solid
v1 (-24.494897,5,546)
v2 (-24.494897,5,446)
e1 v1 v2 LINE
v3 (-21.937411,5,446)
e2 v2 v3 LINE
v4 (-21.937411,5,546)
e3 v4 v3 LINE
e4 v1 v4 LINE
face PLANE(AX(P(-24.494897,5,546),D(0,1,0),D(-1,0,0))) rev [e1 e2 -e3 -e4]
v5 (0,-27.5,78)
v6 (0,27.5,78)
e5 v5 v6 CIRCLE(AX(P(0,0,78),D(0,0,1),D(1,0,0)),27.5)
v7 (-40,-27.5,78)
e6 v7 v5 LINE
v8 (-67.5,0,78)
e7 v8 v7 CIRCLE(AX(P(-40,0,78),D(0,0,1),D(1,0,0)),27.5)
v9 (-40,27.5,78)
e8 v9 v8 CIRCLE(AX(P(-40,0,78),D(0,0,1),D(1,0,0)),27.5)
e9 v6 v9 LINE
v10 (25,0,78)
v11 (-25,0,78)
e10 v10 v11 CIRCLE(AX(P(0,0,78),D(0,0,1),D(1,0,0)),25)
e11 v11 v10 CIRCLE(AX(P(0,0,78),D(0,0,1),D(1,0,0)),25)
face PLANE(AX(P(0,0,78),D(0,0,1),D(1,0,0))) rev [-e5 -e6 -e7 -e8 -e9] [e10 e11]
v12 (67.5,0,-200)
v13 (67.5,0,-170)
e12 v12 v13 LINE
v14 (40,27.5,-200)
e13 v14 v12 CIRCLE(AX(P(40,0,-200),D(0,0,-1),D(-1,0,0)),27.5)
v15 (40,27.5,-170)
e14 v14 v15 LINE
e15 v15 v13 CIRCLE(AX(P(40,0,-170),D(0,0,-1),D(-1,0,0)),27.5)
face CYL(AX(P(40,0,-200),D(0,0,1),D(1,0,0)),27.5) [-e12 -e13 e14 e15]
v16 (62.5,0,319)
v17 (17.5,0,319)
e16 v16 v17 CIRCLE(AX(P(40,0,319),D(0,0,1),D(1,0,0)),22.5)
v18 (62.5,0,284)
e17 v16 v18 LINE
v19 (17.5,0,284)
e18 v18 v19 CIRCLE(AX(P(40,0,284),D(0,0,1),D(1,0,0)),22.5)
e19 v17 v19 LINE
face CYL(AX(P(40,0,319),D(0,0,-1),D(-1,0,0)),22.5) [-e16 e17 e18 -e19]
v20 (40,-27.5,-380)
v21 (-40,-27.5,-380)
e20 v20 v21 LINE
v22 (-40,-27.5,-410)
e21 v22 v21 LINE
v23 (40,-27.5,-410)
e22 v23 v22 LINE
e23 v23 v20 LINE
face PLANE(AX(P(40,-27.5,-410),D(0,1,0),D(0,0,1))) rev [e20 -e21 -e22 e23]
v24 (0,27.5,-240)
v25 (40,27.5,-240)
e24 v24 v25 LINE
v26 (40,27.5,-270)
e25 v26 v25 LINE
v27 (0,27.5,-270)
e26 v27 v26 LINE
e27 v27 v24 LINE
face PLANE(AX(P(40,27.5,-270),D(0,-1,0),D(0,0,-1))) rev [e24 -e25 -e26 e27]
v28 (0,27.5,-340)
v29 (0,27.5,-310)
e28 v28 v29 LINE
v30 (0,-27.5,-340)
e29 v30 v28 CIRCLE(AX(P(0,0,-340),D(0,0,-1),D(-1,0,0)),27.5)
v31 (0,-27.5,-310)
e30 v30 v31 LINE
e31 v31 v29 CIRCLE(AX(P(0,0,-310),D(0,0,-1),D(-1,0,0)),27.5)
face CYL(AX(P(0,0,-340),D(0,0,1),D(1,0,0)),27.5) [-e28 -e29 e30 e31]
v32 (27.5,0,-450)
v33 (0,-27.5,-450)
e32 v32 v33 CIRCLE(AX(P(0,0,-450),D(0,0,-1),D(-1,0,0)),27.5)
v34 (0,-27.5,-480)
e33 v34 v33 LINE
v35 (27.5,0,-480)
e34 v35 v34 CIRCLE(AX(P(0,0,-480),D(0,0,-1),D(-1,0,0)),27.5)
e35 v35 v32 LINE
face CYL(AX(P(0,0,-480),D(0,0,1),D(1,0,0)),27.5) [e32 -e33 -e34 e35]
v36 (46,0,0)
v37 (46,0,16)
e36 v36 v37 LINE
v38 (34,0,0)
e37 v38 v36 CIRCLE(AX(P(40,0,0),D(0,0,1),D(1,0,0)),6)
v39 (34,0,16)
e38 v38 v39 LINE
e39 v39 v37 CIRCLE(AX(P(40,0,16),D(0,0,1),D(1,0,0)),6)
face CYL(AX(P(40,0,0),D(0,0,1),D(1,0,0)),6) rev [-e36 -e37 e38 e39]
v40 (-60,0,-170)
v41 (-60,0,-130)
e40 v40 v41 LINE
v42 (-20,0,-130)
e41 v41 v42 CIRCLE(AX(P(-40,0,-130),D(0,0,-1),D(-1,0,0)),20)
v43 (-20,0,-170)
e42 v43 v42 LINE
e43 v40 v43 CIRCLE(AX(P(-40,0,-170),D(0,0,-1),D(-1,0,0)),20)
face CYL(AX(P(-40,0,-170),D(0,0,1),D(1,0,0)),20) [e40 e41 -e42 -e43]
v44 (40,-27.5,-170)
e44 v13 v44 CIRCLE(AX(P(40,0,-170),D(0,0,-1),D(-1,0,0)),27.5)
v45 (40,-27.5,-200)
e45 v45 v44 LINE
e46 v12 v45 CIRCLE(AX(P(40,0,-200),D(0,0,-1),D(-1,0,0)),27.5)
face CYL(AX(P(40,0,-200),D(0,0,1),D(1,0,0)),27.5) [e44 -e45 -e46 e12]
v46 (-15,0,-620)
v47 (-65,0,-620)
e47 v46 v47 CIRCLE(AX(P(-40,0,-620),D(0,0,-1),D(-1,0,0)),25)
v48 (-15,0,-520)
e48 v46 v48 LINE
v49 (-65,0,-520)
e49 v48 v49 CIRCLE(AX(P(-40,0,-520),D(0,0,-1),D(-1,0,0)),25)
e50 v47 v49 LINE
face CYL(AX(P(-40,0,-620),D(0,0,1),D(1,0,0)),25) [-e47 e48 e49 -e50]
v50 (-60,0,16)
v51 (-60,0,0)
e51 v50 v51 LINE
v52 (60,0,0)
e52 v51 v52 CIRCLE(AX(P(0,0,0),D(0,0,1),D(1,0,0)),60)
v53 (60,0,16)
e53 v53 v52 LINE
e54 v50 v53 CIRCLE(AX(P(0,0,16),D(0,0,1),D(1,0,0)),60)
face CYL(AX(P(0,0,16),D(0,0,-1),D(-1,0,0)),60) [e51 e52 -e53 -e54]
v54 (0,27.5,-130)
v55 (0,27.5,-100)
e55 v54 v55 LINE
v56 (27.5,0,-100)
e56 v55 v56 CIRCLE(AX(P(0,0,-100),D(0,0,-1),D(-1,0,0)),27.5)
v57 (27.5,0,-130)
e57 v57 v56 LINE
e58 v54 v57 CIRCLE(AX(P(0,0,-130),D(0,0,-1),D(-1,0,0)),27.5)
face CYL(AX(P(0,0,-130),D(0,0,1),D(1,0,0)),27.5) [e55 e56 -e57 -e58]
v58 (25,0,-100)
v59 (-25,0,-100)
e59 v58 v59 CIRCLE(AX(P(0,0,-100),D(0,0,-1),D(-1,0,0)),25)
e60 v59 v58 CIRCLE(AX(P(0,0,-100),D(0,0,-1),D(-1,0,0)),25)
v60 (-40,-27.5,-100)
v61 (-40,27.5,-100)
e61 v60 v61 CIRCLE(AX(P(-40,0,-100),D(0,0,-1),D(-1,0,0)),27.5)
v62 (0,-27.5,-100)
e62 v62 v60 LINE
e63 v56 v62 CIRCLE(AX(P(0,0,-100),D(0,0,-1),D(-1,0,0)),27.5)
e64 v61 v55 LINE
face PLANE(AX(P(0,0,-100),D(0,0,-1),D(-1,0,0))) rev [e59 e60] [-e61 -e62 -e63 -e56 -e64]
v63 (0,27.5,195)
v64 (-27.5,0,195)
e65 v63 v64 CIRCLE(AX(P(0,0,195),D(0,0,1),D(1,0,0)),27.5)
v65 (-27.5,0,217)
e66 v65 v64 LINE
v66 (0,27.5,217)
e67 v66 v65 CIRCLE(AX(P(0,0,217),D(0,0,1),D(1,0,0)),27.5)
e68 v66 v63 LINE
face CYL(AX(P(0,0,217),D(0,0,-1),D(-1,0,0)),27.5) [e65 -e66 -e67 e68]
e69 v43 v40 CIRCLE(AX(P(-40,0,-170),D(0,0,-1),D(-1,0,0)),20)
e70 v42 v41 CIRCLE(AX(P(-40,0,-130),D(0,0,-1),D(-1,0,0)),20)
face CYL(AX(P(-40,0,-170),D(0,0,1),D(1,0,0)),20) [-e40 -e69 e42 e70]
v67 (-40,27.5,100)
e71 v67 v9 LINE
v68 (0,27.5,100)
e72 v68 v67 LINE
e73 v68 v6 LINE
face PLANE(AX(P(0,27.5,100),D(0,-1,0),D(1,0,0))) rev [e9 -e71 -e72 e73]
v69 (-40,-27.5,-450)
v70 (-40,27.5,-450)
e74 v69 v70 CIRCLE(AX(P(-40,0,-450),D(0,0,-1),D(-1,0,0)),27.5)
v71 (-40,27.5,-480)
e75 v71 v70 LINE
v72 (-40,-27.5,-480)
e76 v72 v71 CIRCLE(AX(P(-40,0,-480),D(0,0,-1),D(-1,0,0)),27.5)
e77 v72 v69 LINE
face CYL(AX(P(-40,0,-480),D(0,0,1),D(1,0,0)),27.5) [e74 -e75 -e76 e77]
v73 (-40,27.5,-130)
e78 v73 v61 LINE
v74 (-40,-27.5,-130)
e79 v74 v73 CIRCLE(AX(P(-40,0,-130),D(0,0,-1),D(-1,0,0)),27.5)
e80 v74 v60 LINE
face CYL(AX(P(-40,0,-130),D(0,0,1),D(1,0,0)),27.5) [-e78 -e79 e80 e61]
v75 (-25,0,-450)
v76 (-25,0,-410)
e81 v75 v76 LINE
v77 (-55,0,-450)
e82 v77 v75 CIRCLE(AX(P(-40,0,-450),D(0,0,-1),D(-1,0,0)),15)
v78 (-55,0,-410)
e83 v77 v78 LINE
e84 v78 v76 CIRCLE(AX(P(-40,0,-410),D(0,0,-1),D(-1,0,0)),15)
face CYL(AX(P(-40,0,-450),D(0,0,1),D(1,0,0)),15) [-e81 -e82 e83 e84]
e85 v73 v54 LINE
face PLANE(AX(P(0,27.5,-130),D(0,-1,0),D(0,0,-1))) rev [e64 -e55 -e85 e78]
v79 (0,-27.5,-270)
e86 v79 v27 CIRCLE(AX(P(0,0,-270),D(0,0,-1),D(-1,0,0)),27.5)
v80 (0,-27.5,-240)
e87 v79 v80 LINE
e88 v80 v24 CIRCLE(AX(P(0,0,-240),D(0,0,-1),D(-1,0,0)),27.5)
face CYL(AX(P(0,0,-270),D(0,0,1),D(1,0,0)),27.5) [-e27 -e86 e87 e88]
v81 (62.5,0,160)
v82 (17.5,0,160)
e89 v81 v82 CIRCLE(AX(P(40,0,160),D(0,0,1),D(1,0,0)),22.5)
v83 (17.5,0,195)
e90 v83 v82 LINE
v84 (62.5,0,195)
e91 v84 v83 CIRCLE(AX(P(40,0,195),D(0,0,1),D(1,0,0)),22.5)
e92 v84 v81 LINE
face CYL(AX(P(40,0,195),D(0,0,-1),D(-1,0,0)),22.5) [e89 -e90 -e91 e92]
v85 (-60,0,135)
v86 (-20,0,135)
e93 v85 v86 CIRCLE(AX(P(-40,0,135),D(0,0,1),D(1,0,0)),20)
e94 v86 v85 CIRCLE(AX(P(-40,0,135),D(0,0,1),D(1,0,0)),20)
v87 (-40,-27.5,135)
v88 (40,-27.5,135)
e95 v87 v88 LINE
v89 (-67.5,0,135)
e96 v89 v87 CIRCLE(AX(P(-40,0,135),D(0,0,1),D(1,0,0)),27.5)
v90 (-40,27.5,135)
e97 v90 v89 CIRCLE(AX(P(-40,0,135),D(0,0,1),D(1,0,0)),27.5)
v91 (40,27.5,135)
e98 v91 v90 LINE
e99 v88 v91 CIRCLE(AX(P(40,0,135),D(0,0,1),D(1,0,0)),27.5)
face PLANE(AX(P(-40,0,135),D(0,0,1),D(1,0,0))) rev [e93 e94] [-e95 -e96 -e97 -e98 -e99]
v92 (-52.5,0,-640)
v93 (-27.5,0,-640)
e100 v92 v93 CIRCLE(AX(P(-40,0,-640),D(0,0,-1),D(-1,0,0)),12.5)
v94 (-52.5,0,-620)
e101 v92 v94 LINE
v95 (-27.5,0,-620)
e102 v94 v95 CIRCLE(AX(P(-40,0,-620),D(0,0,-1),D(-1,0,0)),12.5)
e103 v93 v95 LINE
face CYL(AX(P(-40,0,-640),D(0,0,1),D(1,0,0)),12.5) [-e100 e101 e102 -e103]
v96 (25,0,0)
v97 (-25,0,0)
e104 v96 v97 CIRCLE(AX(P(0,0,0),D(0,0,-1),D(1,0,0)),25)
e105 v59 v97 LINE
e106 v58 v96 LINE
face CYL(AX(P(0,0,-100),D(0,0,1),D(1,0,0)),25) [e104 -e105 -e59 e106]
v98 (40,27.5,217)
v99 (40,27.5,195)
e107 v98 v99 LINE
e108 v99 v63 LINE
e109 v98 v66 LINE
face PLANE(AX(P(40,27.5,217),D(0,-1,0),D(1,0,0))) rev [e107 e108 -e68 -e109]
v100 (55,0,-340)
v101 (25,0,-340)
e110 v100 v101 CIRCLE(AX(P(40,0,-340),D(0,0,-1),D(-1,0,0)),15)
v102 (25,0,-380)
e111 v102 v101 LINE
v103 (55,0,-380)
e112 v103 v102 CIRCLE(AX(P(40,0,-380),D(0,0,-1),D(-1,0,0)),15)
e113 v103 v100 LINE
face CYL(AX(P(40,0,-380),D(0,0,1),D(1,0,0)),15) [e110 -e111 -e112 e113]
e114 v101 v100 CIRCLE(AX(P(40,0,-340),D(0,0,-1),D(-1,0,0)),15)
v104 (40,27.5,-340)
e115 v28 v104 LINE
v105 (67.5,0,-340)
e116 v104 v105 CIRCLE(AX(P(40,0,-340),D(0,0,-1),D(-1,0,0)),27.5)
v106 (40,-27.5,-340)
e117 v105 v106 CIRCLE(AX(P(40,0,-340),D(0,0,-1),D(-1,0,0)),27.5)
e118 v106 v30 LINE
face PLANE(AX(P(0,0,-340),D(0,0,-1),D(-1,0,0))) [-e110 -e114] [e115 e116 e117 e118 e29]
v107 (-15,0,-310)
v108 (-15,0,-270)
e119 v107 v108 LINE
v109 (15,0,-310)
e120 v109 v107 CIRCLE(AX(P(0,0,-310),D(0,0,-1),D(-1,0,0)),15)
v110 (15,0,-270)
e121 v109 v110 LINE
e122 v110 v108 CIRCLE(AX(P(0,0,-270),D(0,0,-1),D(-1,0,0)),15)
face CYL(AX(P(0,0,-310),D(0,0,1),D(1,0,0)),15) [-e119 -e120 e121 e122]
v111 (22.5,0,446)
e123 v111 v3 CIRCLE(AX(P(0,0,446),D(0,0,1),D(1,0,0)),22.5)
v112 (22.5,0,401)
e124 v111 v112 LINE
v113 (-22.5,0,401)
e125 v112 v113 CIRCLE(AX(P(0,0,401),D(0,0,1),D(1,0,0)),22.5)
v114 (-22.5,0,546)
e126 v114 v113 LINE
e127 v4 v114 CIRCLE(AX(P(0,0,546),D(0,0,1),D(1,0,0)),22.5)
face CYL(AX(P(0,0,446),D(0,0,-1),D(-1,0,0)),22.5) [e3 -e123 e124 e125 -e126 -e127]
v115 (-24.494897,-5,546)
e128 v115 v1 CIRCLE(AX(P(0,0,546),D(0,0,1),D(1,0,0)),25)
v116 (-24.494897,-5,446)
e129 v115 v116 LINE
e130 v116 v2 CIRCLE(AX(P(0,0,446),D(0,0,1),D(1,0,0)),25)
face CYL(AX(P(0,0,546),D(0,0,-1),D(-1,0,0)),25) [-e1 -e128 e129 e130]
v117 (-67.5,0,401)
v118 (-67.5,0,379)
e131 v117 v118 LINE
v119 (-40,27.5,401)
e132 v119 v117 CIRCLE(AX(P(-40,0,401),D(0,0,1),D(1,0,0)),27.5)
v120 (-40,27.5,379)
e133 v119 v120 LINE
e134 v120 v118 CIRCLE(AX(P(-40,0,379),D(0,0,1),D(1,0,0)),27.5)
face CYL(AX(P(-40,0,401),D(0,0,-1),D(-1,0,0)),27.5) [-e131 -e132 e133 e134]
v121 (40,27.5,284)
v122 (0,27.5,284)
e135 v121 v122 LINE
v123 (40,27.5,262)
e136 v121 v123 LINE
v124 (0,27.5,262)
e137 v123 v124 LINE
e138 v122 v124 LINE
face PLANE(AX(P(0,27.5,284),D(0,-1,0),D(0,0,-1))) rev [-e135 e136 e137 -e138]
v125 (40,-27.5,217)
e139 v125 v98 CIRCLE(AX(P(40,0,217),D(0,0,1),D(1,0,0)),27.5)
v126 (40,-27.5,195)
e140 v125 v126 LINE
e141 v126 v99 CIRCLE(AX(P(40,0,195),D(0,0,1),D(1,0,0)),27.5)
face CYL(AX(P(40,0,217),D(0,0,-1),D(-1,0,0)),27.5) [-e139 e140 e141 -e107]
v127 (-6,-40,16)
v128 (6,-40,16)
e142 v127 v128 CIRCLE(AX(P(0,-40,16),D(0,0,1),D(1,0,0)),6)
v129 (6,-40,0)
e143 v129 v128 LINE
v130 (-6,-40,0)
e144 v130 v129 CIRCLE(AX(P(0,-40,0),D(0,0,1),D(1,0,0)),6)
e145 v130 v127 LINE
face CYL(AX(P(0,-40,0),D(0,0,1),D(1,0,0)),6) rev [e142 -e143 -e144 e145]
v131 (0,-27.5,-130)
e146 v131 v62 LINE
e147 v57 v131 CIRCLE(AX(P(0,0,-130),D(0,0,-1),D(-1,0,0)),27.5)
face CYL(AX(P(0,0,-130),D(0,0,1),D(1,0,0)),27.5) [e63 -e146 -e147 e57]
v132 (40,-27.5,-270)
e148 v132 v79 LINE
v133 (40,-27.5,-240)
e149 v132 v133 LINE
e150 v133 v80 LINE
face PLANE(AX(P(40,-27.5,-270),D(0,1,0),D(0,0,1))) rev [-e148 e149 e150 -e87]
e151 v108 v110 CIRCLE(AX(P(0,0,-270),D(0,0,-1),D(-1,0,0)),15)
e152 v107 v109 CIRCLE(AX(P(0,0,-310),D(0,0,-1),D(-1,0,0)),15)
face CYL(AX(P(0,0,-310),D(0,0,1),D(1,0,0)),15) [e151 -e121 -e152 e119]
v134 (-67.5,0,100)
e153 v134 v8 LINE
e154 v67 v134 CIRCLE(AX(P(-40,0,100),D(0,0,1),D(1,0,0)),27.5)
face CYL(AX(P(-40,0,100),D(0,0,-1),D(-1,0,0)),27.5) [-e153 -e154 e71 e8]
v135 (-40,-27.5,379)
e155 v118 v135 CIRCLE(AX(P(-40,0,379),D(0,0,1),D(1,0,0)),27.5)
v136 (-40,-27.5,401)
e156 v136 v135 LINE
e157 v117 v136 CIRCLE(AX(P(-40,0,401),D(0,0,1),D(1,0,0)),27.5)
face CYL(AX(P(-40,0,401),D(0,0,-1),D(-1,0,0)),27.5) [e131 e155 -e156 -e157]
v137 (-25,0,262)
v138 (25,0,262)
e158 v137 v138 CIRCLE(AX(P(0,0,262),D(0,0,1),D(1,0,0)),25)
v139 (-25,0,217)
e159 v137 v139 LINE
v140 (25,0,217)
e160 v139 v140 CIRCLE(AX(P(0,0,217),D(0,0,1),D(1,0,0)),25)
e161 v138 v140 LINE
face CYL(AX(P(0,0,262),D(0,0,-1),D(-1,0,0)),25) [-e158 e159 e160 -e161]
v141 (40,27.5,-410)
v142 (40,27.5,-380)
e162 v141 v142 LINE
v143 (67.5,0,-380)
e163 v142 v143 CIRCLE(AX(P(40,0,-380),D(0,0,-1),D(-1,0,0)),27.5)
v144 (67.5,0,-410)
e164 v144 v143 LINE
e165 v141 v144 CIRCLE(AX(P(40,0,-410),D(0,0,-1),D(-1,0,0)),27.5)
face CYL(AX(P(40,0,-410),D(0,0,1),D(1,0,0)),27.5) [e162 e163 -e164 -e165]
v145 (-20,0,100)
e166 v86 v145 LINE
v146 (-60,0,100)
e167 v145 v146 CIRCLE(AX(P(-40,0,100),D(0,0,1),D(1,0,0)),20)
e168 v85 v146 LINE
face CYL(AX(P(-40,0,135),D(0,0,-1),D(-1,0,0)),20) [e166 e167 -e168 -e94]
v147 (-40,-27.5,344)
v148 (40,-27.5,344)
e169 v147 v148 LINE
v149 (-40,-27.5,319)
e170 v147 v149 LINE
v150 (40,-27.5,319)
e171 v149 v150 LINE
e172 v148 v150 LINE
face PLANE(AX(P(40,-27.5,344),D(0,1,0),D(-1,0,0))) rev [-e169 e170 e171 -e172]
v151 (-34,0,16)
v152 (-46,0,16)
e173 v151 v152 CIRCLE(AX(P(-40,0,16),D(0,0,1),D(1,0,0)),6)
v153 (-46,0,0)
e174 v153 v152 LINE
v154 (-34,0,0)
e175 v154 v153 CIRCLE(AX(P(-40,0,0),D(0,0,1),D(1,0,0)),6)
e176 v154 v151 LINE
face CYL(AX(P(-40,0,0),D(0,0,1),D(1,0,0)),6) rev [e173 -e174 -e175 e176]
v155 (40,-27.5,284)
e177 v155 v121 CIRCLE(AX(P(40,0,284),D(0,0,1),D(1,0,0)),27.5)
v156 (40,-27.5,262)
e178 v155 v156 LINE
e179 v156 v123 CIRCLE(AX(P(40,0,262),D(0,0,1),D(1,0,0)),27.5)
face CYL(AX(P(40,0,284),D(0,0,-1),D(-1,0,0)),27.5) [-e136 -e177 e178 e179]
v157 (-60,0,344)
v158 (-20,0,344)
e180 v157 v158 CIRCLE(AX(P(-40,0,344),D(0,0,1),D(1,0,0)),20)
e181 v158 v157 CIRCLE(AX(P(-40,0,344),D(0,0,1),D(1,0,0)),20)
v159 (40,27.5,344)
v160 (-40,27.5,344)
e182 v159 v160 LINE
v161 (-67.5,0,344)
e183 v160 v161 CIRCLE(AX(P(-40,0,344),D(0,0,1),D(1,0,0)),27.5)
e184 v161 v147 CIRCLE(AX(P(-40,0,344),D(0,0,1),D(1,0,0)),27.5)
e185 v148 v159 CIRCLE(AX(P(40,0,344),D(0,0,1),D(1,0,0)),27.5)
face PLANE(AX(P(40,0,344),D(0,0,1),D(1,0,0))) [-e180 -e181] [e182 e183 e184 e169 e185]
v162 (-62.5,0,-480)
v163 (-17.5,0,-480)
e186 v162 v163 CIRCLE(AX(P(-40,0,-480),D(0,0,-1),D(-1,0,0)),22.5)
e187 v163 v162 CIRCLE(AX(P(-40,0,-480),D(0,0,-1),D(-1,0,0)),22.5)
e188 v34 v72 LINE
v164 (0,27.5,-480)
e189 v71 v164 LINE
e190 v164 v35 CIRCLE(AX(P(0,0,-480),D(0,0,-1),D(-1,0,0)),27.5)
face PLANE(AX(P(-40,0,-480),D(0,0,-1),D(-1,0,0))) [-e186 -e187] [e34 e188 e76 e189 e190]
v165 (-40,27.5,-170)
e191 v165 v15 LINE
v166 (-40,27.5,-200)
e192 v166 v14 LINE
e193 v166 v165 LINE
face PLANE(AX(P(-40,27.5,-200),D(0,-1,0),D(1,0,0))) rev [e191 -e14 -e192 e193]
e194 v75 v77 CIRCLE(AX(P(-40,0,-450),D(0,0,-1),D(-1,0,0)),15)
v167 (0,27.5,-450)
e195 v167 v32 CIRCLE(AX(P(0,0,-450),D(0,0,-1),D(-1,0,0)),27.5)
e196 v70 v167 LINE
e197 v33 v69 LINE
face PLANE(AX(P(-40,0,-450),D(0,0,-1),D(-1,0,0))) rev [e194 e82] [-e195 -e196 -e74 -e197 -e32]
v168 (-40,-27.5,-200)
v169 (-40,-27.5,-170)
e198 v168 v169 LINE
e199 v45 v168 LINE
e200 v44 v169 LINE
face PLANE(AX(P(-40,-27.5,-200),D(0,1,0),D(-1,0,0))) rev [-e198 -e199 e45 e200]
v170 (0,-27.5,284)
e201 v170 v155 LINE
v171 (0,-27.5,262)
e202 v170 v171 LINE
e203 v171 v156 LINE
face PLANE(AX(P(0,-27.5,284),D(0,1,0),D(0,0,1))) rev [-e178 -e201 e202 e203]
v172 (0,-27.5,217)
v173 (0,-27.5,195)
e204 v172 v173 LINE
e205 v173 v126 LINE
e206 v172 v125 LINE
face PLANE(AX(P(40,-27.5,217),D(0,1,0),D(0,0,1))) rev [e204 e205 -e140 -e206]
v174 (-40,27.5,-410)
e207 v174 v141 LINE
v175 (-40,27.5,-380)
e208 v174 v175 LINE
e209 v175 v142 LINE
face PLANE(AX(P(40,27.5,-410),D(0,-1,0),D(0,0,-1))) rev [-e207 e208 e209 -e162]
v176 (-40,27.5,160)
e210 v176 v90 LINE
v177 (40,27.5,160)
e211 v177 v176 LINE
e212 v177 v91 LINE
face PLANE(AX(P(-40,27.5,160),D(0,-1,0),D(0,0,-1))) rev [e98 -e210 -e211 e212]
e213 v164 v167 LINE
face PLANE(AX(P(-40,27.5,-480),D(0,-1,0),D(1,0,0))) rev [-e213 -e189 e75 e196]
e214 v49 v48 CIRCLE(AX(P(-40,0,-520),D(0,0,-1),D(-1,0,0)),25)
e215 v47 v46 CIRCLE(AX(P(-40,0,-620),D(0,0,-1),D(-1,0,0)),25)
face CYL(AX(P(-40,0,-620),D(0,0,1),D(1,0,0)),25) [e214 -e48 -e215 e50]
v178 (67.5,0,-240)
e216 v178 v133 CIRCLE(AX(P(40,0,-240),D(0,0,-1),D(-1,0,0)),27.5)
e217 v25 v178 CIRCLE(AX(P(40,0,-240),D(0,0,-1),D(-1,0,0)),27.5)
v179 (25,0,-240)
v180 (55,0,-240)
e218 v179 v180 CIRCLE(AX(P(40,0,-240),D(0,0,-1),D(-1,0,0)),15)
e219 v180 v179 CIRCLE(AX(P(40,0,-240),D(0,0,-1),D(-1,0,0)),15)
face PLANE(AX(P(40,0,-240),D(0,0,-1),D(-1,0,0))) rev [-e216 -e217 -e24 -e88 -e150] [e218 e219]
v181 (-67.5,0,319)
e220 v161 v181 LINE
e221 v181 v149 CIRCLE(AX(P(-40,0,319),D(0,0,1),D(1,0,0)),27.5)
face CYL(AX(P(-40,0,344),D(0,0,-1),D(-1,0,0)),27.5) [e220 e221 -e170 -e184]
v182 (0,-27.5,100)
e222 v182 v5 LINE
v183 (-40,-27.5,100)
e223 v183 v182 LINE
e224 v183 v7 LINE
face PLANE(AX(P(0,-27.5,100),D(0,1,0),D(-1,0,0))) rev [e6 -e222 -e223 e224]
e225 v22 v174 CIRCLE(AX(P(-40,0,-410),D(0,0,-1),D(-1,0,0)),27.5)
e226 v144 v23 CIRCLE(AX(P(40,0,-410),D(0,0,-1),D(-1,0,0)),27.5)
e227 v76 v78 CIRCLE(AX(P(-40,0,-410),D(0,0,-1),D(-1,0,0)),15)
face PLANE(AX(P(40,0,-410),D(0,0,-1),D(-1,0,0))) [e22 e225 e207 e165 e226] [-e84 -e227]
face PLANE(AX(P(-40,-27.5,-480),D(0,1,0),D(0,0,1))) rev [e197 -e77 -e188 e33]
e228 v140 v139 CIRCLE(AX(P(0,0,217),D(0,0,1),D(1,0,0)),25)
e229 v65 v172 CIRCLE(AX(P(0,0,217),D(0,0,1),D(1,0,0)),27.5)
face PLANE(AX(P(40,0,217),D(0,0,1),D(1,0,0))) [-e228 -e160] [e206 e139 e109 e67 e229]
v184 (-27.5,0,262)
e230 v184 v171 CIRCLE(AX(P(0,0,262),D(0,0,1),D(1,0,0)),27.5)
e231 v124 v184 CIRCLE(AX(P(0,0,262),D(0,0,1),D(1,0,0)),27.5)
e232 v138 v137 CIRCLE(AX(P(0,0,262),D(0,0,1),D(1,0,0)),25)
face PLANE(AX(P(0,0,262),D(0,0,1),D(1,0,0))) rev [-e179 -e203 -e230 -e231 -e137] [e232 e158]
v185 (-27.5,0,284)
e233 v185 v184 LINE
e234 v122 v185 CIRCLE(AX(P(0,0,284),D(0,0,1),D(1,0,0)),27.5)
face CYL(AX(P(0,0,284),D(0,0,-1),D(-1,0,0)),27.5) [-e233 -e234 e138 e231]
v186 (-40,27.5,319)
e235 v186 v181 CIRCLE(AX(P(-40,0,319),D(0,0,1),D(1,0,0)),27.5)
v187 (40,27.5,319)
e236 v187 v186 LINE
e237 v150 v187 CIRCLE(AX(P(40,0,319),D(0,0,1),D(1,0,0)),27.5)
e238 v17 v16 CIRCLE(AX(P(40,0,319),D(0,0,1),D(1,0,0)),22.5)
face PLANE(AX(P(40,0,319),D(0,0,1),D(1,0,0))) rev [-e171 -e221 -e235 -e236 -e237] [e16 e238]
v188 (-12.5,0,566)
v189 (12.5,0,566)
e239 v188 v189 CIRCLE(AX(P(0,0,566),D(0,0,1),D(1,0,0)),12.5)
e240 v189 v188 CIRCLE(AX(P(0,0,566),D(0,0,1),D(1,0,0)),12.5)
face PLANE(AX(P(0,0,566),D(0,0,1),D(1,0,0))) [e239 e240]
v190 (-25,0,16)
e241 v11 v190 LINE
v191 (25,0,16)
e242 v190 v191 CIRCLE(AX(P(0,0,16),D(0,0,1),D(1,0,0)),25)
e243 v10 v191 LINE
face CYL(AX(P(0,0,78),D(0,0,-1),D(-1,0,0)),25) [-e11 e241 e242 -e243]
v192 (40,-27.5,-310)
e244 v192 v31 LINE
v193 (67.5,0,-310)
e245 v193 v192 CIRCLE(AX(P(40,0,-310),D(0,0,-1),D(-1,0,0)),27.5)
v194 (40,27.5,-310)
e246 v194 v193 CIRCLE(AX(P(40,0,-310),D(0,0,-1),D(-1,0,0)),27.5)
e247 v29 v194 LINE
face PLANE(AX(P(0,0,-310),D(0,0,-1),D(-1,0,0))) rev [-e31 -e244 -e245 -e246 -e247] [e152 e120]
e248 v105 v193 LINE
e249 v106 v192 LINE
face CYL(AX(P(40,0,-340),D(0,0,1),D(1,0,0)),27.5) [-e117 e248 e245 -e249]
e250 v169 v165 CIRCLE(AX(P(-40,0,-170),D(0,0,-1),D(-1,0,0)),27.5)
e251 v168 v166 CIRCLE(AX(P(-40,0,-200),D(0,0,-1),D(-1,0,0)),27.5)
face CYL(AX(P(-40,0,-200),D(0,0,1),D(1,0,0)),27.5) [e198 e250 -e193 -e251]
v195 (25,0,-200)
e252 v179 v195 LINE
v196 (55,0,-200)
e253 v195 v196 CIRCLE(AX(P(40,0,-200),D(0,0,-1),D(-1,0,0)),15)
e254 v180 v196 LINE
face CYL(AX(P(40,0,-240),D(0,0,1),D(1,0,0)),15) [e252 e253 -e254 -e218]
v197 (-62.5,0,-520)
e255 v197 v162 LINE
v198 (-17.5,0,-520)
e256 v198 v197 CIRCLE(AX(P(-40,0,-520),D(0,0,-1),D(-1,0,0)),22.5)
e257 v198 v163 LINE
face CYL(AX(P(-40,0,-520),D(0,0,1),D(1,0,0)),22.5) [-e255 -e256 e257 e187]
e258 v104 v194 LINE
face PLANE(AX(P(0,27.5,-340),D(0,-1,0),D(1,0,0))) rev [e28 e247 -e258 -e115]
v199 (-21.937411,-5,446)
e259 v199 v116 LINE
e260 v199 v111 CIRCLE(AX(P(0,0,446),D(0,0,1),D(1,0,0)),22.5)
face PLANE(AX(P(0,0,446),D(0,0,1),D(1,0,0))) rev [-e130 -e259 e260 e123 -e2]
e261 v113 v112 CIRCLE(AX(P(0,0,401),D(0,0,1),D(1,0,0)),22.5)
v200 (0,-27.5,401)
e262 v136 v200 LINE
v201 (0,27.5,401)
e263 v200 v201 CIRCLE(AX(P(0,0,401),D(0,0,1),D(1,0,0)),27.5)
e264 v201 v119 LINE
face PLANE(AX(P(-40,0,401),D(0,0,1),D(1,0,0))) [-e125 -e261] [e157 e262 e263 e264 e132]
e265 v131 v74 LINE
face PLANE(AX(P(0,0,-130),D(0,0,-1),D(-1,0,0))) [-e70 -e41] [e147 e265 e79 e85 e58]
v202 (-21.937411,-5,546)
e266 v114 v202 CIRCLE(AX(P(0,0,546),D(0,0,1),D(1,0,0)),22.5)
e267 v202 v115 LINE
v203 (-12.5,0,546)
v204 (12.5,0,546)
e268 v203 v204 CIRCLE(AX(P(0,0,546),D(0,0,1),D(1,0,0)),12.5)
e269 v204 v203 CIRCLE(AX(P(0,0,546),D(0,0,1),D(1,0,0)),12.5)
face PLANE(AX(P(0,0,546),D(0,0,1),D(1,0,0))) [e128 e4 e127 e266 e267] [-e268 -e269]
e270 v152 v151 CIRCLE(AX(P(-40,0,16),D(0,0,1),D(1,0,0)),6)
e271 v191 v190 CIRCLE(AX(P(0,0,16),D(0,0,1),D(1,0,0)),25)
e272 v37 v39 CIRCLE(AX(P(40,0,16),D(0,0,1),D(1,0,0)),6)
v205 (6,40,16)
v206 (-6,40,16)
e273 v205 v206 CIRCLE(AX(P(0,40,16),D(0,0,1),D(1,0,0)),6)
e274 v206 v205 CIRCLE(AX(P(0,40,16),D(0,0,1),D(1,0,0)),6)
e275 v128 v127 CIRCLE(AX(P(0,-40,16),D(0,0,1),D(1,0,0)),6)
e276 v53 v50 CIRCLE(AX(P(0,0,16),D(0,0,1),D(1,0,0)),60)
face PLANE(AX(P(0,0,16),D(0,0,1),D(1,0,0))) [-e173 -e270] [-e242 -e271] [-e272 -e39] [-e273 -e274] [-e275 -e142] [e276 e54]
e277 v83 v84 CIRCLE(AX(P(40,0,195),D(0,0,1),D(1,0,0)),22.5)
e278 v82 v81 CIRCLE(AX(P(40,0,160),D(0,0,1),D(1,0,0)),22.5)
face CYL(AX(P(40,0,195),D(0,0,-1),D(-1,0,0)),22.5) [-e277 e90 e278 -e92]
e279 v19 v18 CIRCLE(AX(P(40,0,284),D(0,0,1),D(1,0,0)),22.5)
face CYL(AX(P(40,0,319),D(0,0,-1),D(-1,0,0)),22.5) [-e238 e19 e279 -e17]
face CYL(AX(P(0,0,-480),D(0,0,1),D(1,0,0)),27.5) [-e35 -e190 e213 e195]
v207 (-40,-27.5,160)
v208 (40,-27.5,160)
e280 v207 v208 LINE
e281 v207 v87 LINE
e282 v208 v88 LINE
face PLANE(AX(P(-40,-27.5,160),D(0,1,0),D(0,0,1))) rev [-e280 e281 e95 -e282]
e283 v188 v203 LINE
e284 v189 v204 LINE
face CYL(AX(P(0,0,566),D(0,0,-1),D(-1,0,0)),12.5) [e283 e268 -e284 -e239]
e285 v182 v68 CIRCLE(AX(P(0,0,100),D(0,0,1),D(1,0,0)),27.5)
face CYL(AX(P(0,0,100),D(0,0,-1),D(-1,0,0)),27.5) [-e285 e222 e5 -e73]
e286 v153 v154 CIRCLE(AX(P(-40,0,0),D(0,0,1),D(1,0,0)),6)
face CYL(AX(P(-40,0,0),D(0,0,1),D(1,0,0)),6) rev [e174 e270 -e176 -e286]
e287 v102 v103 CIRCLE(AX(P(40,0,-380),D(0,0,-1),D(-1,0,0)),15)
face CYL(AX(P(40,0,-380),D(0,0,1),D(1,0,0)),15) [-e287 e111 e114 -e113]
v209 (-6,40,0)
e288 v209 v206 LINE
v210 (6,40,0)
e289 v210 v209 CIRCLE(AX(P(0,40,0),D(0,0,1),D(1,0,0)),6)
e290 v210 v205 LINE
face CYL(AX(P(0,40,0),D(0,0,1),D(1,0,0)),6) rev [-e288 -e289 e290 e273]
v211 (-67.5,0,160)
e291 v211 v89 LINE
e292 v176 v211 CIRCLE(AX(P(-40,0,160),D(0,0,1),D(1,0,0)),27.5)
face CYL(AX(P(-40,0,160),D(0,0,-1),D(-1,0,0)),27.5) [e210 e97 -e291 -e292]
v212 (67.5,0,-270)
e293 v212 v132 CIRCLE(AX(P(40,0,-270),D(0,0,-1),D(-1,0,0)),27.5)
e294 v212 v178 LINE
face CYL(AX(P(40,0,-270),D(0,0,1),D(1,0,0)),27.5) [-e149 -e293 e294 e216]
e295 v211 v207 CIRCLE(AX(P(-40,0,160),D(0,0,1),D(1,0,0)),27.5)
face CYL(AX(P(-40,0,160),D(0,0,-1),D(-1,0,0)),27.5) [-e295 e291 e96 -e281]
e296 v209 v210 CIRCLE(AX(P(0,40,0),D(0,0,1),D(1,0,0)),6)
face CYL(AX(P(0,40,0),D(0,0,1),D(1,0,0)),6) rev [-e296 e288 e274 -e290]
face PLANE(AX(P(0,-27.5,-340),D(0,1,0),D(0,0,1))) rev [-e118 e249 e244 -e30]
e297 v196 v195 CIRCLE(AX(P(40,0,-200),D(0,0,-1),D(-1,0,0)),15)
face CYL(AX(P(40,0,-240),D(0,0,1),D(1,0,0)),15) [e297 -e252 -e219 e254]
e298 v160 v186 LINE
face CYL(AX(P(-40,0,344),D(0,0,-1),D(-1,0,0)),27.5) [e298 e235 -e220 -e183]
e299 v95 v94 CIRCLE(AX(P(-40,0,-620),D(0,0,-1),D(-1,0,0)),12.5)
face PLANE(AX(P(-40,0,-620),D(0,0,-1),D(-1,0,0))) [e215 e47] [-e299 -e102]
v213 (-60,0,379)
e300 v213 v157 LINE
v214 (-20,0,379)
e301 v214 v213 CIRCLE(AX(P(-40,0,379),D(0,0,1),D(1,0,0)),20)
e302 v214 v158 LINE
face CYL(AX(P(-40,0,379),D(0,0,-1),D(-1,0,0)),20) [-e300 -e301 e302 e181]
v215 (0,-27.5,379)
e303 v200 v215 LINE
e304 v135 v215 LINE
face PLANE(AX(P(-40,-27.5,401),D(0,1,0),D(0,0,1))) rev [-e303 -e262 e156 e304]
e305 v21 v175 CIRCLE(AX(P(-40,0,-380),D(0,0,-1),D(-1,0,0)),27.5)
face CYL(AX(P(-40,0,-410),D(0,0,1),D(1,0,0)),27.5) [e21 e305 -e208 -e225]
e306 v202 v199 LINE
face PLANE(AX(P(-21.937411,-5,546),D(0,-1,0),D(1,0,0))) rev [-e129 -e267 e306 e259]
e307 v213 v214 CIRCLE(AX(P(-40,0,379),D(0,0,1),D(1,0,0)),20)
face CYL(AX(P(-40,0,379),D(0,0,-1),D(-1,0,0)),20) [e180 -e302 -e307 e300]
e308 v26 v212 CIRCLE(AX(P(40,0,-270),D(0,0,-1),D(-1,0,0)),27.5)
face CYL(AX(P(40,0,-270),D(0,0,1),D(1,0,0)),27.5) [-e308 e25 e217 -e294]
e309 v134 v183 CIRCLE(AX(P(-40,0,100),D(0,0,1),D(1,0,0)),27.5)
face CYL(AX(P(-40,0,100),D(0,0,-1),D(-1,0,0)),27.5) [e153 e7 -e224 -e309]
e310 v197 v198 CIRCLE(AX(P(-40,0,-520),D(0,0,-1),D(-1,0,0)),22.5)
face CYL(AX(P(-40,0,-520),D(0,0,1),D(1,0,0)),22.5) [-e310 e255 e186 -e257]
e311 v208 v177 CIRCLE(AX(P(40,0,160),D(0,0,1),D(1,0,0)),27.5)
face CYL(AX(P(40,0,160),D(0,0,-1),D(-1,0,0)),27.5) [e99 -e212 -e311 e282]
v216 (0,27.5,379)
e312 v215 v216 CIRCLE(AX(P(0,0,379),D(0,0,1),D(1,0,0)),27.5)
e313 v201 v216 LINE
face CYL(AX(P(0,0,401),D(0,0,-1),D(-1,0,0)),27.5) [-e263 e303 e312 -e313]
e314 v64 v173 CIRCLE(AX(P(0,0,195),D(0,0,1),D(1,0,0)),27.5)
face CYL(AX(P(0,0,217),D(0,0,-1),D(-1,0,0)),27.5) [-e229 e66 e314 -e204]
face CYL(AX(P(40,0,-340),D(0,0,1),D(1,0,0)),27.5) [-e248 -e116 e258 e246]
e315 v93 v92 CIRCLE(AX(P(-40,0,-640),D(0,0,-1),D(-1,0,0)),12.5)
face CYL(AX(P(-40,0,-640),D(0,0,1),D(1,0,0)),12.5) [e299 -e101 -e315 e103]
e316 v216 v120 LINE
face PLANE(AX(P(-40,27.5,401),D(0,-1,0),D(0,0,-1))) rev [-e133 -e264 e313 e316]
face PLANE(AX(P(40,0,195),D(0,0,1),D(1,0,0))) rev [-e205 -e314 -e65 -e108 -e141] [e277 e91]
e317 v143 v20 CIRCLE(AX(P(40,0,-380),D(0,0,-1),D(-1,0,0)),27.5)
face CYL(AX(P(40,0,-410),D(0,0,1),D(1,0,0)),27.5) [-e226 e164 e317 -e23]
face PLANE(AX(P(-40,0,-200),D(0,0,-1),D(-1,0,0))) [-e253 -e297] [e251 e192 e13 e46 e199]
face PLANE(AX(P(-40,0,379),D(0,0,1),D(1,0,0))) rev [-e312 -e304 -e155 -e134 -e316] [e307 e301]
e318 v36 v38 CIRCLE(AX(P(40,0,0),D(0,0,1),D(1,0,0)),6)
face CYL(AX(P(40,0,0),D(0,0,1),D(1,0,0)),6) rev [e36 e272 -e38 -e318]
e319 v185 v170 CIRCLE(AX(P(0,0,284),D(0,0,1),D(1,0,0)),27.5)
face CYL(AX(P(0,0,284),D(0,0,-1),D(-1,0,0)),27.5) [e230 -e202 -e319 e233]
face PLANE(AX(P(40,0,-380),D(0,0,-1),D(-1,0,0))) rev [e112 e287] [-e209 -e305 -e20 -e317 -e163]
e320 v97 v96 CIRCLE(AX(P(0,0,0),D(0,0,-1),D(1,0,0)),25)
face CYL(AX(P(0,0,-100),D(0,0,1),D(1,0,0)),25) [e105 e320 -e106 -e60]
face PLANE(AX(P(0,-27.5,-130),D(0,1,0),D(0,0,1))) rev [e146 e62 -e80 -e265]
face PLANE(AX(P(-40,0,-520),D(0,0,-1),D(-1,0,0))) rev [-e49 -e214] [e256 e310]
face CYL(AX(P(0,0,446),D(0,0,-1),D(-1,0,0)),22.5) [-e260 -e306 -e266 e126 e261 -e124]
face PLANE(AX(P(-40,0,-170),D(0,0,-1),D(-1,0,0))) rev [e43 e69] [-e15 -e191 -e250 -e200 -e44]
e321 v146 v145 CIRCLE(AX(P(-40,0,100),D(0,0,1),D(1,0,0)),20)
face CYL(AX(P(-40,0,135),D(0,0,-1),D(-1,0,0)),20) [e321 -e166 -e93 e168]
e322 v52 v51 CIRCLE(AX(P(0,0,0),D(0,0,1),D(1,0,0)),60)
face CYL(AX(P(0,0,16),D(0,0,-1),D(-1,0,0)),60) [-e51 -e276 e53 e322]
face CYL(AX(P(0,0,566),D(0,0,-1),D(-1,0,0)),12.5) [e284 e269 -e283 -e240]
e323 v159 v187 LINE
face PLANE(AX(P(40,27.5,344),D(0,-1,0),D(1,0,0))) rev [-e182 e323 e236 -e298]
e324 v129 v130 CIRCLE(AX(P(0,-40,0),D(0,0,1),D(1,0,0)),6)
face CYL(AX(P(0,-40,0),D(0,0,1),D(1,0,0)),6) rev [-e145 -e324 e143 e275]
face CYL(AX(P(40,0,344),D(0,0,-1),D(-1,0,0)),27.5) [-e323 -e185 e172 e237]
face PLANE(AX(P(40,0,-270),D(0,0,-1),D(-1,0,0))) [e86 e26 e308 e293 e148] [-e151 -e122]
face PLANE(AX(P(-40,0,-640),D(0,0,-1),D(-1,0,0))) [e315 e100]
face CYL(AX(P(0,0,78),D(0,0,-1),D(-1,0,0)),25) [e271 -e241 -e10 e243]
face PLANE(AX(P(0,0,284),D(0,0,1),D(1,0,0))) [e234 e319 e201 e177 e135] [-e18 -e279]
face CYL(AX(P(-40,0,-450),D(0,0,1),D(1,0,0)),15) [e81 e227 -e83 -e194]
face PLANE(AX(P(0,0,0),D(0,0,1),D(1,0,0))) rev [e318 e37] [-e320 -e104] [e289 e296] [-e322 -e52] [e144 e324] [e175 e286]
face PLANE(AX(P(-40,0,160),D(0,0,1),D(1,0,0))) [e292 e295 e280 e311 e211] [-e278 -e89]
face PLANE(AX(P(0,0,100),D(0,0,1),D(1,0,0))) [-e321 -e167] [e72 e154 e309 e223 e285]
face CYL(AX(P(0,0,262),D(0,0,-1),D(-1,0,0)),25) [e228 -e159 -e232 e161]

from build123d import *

# Parameters (mm, degrees)
CENTRE_FLANGE_SKETCH_R  = 60
CENTRE_FLANGE_120_DEPTH = 16
FLANGE_HOLES_SKETCH_R   = 6
FLANGE_HOLES_12_DEPTH   = 87.34813258
A_JOURNAL_1_SKETCH_R    = 25
A_JOURNAL_1_50_DEPTH    = 62
A_WEB_1_DEPTH           = 22
A_PIN_1_SKETCH_R        = 20
A_PIN_1_40_DEPTH        = 35
A_WEB_2_DEPTH           = 25
A_PIN_2_SKETCH_R        = 22.5
A_PIN_2_45_DEPTH        = 35
A_WEB_3_DEPTH           = 22
A_JOURNAL_2_SKETCH_R    = 25
A_JOURNAL_2_50_DEPTH    = 45
A_WEB_4_DEPTH           = 22
A_PIN_3_SKETCH_R        = 22.5
A_PIN_3_45_DEPTH        = 35
A_WEB_5_DEPTH           = 25
A_PIN_4_SKETCH_R        = 20
A_PIN_4_40_DEPTH        = 35
A_WEB_6_DEPTH           = 22
A_JOURNAL_3_SKETCH_R    = 22.5
A_JOURNAL_3_45_DEPTH    = 45
A_SHAFT_END_DEPTH       = 100
A_END_SPIGOT_SKETCH_R   = 12.5
A_END_SPIGOT_25_DEPTH   = 20
B_START                 = 100
B_JOURNAL_1_SKETCH_R    = 25
B_JOURNAL_1_50_DEPTH    = 100
B_START_2               = 30
B_WEB_1_DEPTH           = 30
B_START_3               = 40
B_PIN_1_SKETCH_R        = 20
B_PIN_1_40_DEPTH        = 40
B_WEB_2_DEPTH           = 30
B_JOURNAL_2_SKETCH_R    = 15
B_JOURNAL_2_30_DEPTH    = 40
B_WEB_3_DEPTH           = 30
B_JOURNAL_3_SKETCH_R    = 15
B_JOURNAL_3_30_DEPTH    = 40
B_WEB_4_DEPTH           = 30
B_JOURNAL_4_SKETCH_R    = 15
B_JOURNAL_4_30_DEPTH    = 40
B_WEB_5_DEPTH           = 30
B_JOURNAL_5_SKETCH_R    = 15
B_JOURNAL_5_30_DEPTH    = 40
B_WEB_6_DEPTH           = 30
B_JOURNAL_6_SKETCH_R    = 22.5
B_JOURNAL_6_45_DEPTH    = 40
B_SHAFT_END_SKETCH_R    = 25
B_SHAFT_END_50_DEPTH    = 100
B_END_SPIGOT_SKETCH_R   = 12.5
B_END_SPIGOT_25_DEPTH   = 20


with BuildPart() as part:
    # Centre Flange Sketch → Centre Flange Ø120 (new body)
    with BuildSketch(Plane.XY):
        Circle(CENTRE_FLANGE_SKETCH_R)
    extrude(amount=CENTRE_FLANGE_120_DEPTH)

    # Flange Holes Sketch → Flange Holes Ø12 (cut, through all)
    with BuildSketch(Plane.XY.offset(16)):
        with Locations((0, 40)):
            Circle(FLANGE_HOLES_SKETCH_R)
        with Locations((40, 0)):
            Circle(FLANGE_HOLES_SKETCH_R)
        with Locations((0, -40)):
            Circle(FLANGE_HOLES_SKETCH_R)
        with Locations((-40, 0)):
            Circle(FLANGE_HOLES_SKETCH_R)
    extrude(amount=-FLANGE_HOLES_12_DEPTH, mode=Mode.SUBTRACT)

    # A Journal 1 Sketch → A Journal 1 Ø50 (add)
    with BuildSketch(Plane.XY.offset(16)):
        Circle(A_JOURNAL_1_SKETCH_R)
    extrude(amount=A_JOURNAL_1_50_DEPTH)

    # A Web 1 Sketch → A Web 1 (add)
    with BuildSketch(Plane.XY.offset(78)):
        with BuildLine():
            Line((0, -27.5), (-40, -27.5))
            ThreePointArc((-40, -27.5), (-67.5, 0), (-40, 27.5))
            Line((-40, 27.5), (0, 27.5))
            ThreePointArc((0, 27.5), (27.5, 0), (0, -27.5))
        make_face()
    extrude(amount=A_WEB_1_DEPTH)

    # A Pin 1 Sketch → A Pin 1 Ø40 (add)
    with BuildSketch(Plane.XY.offset(100)):
        with Locations((-40, 0)):
            Circle(A_PIN_1_SKETCH_R)
    extrude(amount=A_PIN_1_40_DEPTH)

    # A Web 2 Sketch → A Web 2 (add)
    with BuildSketch(Plane.XY.offset(135)):
        with BuildLine():
            Line((-40, 27.5), (40, 27.5))
            ThreePointArc((40, 27.5), (67.5, 0), (40, -27.5))
            Line((40, -27.5), (-40, -27.5))
            ThreePointArc((-40, -27.5), (-67.5, 0), (-40, 27.5))
        make_face()
    extrude(amount=A_WEB_2_DEPTH)

    # A Pin 2 Sketch → A Pin 2 Ø45 (add)
    with BuildSketch(Plane.XY.offset(160)):
        with Locations((40, 0)):
            Circle(A_PIN_2_SKETCH_R)
    extrude(amount=A_PIN_2_45_DEPTH)

    # A Web 3 Sketch → A Web 3 (add)
    with BuildSketch(Plane.XY.offset(195)):
        with BuildLine():
            Line((40, -27.5), (0, -27.5))
            ThreePointArc((0, -27.5), (-27.5, 0), (0, 27.5))
            Line((0, 27.5), (40, 27.5))
            ThreePointArc((40, 27.5), (67.5, 0), (40, -27.5))
        make_face()
    extrude(amount=A_WEB_3_DEPTH)

    # A Journal 2 Sketch → A Journal 2 Ø50 (add)
    with BuildSketch(Plane.XY.offset(217)):
        Circle(A_JOURNAL_2_SKETCH_R)
    extrude(amount=A_JOURNAL_2_50_DEPTH)

    # A Web 4 Sketch → A Web 4 (add)
    with BuildSketch(Plane.XY.offset(262)):
        with BuildLine():
            Line((0, 27.5), (40, 27.5))
            ThreePointArc((40, 27.5), (67.5, 0), (40, -27.5))
            Line((40, -27.5), (0, -27.5))
            ThreePointArc((0, -27.5), (-27.5, 0), (0, 27.5))
        make_face()
    extrude(amount=A_WEB_4_DEPTH)

    # A Pin 3 Sketch → A Pin 3 Ø45 (add)
    with BuildSketch(Plane.XY.offset(284)):
        with Locations((40, 0)):
            Circle(A_PIN_3_SKETCH_R)
    extrude(amount=A_PIN_3_45_DEPTH)

    # A Web 5 Sketch → A Web 5 (add)
    with BuildSketch(Plane.XY.offset(319)):
        with BuildLine():
            Line((40, -27.5), (-40, -27.5))
            ThreePointArc((-40, -27.5), (-67.5, 0), (-40, 27.5))
            Line((-40, 27.5), (40, 27.5))
            ThreePointArc((40, 27.5), (67.5, 0), (40, -27.5))
        make_face()
    extrude(amount=A_WEB_5_DEPTH)

    # A Pin 4 Sketch → A Pin 4 Ø40 (add)
    with BuildSketch(Plane.XY.offset(344)):
        with Locations((-40, 0)):
            Circle(A_PIN_4_SKETCH_R)
    extrude(amount=A_PIN_4_40_DEPTH)

    # A Web 6 Sketch → A Web 6 (add)
    with BuildSketch(Plane.XY.offset(379)):
        with BuildLine():
            Line((-40, 27.5), (0, 27.5))
            ThreePointArc((0, 27.5), (27.5, 0), (0, -27.5))
            Line((0, -27.5), (-40, -27.5))
            ThreePointArc((-40, -27.5), (-67.5, 0), (-40, 27.5))
        make_face()
    extrude(amount=A_WEB_6_DEPTH)

    # A Journal 3 Sketch → A Journal 3 Ø45 (add)
    with BuildSketch(Plane.XY.offset(401)):
        with Locations(Location((0, 0, 0), (0, 0, 180))):
            Circle(A_JOURNAL_3_SKETCH_R)
    extrude(amount=A_JOURNAL_3_45_DEPTH)

    # A Shaft End Sketch → A Shaft End (add)
    with BuildSketch(Plane.XY.offset(446)):
        with BuildLine():
            Line((-24.494897428, 5), (-21.937410968, 5))
            ThreePointArc((-21.937410968, 5), (-22.5, 0), (-21.937410968, -5))
            Line((-21.937410968, -5), (-24.494897428, -5))
            ThreePointArc((-24.494897428, -5), (25, 0), (-24.494897428, 5))
        make_face()
    extrude(amount=A_SHAFT_END_DEPTH)

    # A End Spigot Sketch → A End Spigot Ø25 (add)
    with BuildSketch(Plane.XY.offset(546)):
        Circle(A_END_SPIGOT_SKETCH_R)
    extrude(amount=A_END_SPIGOT_25_DEPTH)

    # B Journal 1 Sketch → B Journal 1 Ø50 (add)
    with BuildSketch(Plane(origin=(0, 0, 0), x_dir=(-1, 0, 0), z_dir=(0, 0, -1)).offset(B_START)):
        with Locations(Location((0, 0, 0), (0, 0, 180))):
            Circle(B_JOURNAL_1_SKETCH_R)
    extrude(amount=-B_JOURNAL_1_50_DEPTH)

    # B Web 1 Sketch → B Web 1 (add)
    with BuildSketch(Plane(origin=(0, 0, -100), x_dir=(-1, 0, 0), z_dir=(0, 0, -1)).offset(B_START_2)):
        with BuildLine():
            Line((0, 27.5), (40, 27.5))
            ThreePointArc((40, 27.5), (67.5, 0), (40, -27.5))
            Line((40, -27.5), (0, -27.5))
            ThreePointArc((0, -27.5), (-27.5, 0), (0, 27.5))
        make_face()
    extrude(amount=-B_WEB_1_DEPTH)

    # B Pin 1 Sketch → B Pin 1 Ø40 (add)
    with BuildSketch(Plane(origin=(0, 0, -130), x_dir=(-1, 0, 0), z_dir=(0, 0, -1)).offset(B_START_3)):
        with Locations(Location((40, 0, 0), (0, 0, 180))):
            Circle(B_PIN_1_SKETCH_R)
    extrude(amount=-B_PIN_1_40_DEPTH)

    # B Web 2 Sketch → B Web 2 (add)
    with BuildSketch(Plane(origin=(0, 0, -170), x_dir=(-1, 0, 0), z_dir=(0, 0, -1)).offset(B_START_2)):
        with BuildLine():
            Line((40, -27.5), (-40, -27.5))
            ThreePointArc((-40, -27.5), (-67.5, 0), (-40, 27.5))
            Line((-40, 27.5), (40, 27.5))
            ThreePointArc((40, 27.5), (67.5, 0), (40, -27.5))
        make_face()
    extrude(amount=-B_WEB_2_DEPTH)

    # B Journal 2 Sketch → B Journal 2 Ø30 (add)
    with BuildSketch(Plane(origin=(0, 0, -200), x_dir=(-1, 0, 0), z_dir=(0, 0, -1))):
        with Locations((-40, 0)):
            Circle(B_JOURNAL_2_SKETCH_R)
    extrude(amount=B_JOURNAL_2_30_DEPTH)

    # B Web 3 Sketch → B Web 3 (add)
    with BuildSketch(Plane(origin=(0, 0, -240), x_dir=(-1, 0, 0), z_dir=(0, 0, -1)).offset(B_START_2)):
        with BuildLine():
            Line((-40, 27.5), (0, 27.5))
            ThreePointArc((0, 27.5), (27.5, 0), (0, -27.5))
            Line((0, -27.5), (-40, -27.5))
            ThreePointArc((-40, -27.5), (-67.5, 0), (-40, 27.5))
        make_face()
    extrude(amount=-B_WEB_3_DEPTH)

    # B Journal 3 Sketch → B Journal 3 Ø30 (add)
    with BuildSketch(Plane(origin=(0, 0, -270), x_dir=(-1, 0, 0), z_dir=(0, 0, -1))):
        Circle(B_JOURNAL_3_SKETCH_R)
    extrude(amount=B_JOURNAL_3_30_DEPTH)

    # B Web 4 Sketch → B Web 4 (add)
    with BuildSketch(Plane(origin=(0, 0, -310), x_dir=(-1, 0, 0), z_dir=(0, 0, -1)).offset(B_START_2)):
        with BuildLine():
            Line((0, -27.5), (-40, -27.5))
            ThreePointArc((-40, -27.5), (-67.5, 0), (-40, 27.5))
            Line((-40, 27.5), (0, 27.5))
            ThreePointArc((0, 27.5), (27.5, 0), (0, -27.5))
        make_face()
    extrude(amount=-B_WEB_4_DEPTH)

    # B Journal 4 Sketch → B Journal 4 Ø30 (add)
    with BuildSketch(Plane(origin=(0, 0, -340), x_dir=(-1, 0, 0), z_dir=(0, 0, -1))):
        with Locations((-40, 0)):
            Circle(B_JOURNAL_4_SKETCH_R)
    extrude(amount=B_JOURNAL_4_30_DEPTH)

    # B Web 5 Sketch → B Web 5 (add)
    with BuildSketch(Plane(origin=(0, 0, -380), x_dir=(-1, 0, 0), z_dir=(0, 0, -1)).offset(B_START_2)):
        with BuildLine():
            Line((-40, 27.5), (40, 27.5))
            ThreePointArc((40, 27.5), (67.5, 0), (40, -27.5))
            Line((40, -27.5), (-40, -27.5))
            ThreePointArc((-40, -27.5), (-67.5, 0), (-40, 27.5))
        make_face()
    extrude(amount=-B_WEB_5_DEPTH)

    # B Journal 5 Sketch → B Journal 5 Ø30 (add)
    with BuildSketch(Plane(origin=(0, 0, -410), x_dir=(-1, 0, 0), z_dir=(0, 0, -1))):
        with Locations((40, 0)):
            Circle(B_JOURNAL_5_SKETCH_R)
    extrude(amount=B_JOURNAL_5_30_DEPTH)

    # B Web 6 Sketch → B Web 6 (add)
    with BuildSketch(Plane(origin=(0, 0, -450), x_dir=(-1, 0, 0), z_dir=(0, 0, -1)).offset(B_START_2)):
        with BuildLine():
            Line((40, -27.5), (0, -27.5))
            ThreePointArc((0, -27.5), (-27.5, 0), (0, 27.5))
            Line((0, 27.5), (40, 27.5))
            ThreePointArc((40, 27.5), (67.5, 0), (40, -27.5))
        make_face()
    extrude(amount=-B_WEB_6_DEPTH)

    # B Journal 6 Sketch → B Journal 6 Ø45 (add)
    with BuildSketch(Plane(origin=(0, 0, -480), x_dir=(-1, 0, 0), z_dir=(0, 0, -1))):
        with Locations((40, 0)):
            Circle(B_JOURNAL_6_SKETCH_R)
    extrude(amount=B_JOURNAL_6_45_DEPTH)

    # B Shaft End Sketch → B Shaft End Ø50 (add)
    with BuildSketch(Plane(origin=(0, 0, -520), x_dir=(-1, 0, 0), z_dir=(0, 0, -1))):
        with Locations((40, 0)):
            Circle(B_SHAFT_END_SKETCH_R)
    extrude(amount=B_SHAFT_END_50_DEPTH)

    # B End Spigot Sketch → B End Spigot Ø25 (add)
    with BuildSketch(Plane(origin=(0, 0, -620), x_dir=(-1, 0, 0), z_dir=(0, 0, -1))):
        with Locations((40, 0)):
            Circle(B_END_SPIGOT_SKETCH_R)
    extrude(amount=B_END_SPIGOT_25_DEPTH)


solid = part.part
